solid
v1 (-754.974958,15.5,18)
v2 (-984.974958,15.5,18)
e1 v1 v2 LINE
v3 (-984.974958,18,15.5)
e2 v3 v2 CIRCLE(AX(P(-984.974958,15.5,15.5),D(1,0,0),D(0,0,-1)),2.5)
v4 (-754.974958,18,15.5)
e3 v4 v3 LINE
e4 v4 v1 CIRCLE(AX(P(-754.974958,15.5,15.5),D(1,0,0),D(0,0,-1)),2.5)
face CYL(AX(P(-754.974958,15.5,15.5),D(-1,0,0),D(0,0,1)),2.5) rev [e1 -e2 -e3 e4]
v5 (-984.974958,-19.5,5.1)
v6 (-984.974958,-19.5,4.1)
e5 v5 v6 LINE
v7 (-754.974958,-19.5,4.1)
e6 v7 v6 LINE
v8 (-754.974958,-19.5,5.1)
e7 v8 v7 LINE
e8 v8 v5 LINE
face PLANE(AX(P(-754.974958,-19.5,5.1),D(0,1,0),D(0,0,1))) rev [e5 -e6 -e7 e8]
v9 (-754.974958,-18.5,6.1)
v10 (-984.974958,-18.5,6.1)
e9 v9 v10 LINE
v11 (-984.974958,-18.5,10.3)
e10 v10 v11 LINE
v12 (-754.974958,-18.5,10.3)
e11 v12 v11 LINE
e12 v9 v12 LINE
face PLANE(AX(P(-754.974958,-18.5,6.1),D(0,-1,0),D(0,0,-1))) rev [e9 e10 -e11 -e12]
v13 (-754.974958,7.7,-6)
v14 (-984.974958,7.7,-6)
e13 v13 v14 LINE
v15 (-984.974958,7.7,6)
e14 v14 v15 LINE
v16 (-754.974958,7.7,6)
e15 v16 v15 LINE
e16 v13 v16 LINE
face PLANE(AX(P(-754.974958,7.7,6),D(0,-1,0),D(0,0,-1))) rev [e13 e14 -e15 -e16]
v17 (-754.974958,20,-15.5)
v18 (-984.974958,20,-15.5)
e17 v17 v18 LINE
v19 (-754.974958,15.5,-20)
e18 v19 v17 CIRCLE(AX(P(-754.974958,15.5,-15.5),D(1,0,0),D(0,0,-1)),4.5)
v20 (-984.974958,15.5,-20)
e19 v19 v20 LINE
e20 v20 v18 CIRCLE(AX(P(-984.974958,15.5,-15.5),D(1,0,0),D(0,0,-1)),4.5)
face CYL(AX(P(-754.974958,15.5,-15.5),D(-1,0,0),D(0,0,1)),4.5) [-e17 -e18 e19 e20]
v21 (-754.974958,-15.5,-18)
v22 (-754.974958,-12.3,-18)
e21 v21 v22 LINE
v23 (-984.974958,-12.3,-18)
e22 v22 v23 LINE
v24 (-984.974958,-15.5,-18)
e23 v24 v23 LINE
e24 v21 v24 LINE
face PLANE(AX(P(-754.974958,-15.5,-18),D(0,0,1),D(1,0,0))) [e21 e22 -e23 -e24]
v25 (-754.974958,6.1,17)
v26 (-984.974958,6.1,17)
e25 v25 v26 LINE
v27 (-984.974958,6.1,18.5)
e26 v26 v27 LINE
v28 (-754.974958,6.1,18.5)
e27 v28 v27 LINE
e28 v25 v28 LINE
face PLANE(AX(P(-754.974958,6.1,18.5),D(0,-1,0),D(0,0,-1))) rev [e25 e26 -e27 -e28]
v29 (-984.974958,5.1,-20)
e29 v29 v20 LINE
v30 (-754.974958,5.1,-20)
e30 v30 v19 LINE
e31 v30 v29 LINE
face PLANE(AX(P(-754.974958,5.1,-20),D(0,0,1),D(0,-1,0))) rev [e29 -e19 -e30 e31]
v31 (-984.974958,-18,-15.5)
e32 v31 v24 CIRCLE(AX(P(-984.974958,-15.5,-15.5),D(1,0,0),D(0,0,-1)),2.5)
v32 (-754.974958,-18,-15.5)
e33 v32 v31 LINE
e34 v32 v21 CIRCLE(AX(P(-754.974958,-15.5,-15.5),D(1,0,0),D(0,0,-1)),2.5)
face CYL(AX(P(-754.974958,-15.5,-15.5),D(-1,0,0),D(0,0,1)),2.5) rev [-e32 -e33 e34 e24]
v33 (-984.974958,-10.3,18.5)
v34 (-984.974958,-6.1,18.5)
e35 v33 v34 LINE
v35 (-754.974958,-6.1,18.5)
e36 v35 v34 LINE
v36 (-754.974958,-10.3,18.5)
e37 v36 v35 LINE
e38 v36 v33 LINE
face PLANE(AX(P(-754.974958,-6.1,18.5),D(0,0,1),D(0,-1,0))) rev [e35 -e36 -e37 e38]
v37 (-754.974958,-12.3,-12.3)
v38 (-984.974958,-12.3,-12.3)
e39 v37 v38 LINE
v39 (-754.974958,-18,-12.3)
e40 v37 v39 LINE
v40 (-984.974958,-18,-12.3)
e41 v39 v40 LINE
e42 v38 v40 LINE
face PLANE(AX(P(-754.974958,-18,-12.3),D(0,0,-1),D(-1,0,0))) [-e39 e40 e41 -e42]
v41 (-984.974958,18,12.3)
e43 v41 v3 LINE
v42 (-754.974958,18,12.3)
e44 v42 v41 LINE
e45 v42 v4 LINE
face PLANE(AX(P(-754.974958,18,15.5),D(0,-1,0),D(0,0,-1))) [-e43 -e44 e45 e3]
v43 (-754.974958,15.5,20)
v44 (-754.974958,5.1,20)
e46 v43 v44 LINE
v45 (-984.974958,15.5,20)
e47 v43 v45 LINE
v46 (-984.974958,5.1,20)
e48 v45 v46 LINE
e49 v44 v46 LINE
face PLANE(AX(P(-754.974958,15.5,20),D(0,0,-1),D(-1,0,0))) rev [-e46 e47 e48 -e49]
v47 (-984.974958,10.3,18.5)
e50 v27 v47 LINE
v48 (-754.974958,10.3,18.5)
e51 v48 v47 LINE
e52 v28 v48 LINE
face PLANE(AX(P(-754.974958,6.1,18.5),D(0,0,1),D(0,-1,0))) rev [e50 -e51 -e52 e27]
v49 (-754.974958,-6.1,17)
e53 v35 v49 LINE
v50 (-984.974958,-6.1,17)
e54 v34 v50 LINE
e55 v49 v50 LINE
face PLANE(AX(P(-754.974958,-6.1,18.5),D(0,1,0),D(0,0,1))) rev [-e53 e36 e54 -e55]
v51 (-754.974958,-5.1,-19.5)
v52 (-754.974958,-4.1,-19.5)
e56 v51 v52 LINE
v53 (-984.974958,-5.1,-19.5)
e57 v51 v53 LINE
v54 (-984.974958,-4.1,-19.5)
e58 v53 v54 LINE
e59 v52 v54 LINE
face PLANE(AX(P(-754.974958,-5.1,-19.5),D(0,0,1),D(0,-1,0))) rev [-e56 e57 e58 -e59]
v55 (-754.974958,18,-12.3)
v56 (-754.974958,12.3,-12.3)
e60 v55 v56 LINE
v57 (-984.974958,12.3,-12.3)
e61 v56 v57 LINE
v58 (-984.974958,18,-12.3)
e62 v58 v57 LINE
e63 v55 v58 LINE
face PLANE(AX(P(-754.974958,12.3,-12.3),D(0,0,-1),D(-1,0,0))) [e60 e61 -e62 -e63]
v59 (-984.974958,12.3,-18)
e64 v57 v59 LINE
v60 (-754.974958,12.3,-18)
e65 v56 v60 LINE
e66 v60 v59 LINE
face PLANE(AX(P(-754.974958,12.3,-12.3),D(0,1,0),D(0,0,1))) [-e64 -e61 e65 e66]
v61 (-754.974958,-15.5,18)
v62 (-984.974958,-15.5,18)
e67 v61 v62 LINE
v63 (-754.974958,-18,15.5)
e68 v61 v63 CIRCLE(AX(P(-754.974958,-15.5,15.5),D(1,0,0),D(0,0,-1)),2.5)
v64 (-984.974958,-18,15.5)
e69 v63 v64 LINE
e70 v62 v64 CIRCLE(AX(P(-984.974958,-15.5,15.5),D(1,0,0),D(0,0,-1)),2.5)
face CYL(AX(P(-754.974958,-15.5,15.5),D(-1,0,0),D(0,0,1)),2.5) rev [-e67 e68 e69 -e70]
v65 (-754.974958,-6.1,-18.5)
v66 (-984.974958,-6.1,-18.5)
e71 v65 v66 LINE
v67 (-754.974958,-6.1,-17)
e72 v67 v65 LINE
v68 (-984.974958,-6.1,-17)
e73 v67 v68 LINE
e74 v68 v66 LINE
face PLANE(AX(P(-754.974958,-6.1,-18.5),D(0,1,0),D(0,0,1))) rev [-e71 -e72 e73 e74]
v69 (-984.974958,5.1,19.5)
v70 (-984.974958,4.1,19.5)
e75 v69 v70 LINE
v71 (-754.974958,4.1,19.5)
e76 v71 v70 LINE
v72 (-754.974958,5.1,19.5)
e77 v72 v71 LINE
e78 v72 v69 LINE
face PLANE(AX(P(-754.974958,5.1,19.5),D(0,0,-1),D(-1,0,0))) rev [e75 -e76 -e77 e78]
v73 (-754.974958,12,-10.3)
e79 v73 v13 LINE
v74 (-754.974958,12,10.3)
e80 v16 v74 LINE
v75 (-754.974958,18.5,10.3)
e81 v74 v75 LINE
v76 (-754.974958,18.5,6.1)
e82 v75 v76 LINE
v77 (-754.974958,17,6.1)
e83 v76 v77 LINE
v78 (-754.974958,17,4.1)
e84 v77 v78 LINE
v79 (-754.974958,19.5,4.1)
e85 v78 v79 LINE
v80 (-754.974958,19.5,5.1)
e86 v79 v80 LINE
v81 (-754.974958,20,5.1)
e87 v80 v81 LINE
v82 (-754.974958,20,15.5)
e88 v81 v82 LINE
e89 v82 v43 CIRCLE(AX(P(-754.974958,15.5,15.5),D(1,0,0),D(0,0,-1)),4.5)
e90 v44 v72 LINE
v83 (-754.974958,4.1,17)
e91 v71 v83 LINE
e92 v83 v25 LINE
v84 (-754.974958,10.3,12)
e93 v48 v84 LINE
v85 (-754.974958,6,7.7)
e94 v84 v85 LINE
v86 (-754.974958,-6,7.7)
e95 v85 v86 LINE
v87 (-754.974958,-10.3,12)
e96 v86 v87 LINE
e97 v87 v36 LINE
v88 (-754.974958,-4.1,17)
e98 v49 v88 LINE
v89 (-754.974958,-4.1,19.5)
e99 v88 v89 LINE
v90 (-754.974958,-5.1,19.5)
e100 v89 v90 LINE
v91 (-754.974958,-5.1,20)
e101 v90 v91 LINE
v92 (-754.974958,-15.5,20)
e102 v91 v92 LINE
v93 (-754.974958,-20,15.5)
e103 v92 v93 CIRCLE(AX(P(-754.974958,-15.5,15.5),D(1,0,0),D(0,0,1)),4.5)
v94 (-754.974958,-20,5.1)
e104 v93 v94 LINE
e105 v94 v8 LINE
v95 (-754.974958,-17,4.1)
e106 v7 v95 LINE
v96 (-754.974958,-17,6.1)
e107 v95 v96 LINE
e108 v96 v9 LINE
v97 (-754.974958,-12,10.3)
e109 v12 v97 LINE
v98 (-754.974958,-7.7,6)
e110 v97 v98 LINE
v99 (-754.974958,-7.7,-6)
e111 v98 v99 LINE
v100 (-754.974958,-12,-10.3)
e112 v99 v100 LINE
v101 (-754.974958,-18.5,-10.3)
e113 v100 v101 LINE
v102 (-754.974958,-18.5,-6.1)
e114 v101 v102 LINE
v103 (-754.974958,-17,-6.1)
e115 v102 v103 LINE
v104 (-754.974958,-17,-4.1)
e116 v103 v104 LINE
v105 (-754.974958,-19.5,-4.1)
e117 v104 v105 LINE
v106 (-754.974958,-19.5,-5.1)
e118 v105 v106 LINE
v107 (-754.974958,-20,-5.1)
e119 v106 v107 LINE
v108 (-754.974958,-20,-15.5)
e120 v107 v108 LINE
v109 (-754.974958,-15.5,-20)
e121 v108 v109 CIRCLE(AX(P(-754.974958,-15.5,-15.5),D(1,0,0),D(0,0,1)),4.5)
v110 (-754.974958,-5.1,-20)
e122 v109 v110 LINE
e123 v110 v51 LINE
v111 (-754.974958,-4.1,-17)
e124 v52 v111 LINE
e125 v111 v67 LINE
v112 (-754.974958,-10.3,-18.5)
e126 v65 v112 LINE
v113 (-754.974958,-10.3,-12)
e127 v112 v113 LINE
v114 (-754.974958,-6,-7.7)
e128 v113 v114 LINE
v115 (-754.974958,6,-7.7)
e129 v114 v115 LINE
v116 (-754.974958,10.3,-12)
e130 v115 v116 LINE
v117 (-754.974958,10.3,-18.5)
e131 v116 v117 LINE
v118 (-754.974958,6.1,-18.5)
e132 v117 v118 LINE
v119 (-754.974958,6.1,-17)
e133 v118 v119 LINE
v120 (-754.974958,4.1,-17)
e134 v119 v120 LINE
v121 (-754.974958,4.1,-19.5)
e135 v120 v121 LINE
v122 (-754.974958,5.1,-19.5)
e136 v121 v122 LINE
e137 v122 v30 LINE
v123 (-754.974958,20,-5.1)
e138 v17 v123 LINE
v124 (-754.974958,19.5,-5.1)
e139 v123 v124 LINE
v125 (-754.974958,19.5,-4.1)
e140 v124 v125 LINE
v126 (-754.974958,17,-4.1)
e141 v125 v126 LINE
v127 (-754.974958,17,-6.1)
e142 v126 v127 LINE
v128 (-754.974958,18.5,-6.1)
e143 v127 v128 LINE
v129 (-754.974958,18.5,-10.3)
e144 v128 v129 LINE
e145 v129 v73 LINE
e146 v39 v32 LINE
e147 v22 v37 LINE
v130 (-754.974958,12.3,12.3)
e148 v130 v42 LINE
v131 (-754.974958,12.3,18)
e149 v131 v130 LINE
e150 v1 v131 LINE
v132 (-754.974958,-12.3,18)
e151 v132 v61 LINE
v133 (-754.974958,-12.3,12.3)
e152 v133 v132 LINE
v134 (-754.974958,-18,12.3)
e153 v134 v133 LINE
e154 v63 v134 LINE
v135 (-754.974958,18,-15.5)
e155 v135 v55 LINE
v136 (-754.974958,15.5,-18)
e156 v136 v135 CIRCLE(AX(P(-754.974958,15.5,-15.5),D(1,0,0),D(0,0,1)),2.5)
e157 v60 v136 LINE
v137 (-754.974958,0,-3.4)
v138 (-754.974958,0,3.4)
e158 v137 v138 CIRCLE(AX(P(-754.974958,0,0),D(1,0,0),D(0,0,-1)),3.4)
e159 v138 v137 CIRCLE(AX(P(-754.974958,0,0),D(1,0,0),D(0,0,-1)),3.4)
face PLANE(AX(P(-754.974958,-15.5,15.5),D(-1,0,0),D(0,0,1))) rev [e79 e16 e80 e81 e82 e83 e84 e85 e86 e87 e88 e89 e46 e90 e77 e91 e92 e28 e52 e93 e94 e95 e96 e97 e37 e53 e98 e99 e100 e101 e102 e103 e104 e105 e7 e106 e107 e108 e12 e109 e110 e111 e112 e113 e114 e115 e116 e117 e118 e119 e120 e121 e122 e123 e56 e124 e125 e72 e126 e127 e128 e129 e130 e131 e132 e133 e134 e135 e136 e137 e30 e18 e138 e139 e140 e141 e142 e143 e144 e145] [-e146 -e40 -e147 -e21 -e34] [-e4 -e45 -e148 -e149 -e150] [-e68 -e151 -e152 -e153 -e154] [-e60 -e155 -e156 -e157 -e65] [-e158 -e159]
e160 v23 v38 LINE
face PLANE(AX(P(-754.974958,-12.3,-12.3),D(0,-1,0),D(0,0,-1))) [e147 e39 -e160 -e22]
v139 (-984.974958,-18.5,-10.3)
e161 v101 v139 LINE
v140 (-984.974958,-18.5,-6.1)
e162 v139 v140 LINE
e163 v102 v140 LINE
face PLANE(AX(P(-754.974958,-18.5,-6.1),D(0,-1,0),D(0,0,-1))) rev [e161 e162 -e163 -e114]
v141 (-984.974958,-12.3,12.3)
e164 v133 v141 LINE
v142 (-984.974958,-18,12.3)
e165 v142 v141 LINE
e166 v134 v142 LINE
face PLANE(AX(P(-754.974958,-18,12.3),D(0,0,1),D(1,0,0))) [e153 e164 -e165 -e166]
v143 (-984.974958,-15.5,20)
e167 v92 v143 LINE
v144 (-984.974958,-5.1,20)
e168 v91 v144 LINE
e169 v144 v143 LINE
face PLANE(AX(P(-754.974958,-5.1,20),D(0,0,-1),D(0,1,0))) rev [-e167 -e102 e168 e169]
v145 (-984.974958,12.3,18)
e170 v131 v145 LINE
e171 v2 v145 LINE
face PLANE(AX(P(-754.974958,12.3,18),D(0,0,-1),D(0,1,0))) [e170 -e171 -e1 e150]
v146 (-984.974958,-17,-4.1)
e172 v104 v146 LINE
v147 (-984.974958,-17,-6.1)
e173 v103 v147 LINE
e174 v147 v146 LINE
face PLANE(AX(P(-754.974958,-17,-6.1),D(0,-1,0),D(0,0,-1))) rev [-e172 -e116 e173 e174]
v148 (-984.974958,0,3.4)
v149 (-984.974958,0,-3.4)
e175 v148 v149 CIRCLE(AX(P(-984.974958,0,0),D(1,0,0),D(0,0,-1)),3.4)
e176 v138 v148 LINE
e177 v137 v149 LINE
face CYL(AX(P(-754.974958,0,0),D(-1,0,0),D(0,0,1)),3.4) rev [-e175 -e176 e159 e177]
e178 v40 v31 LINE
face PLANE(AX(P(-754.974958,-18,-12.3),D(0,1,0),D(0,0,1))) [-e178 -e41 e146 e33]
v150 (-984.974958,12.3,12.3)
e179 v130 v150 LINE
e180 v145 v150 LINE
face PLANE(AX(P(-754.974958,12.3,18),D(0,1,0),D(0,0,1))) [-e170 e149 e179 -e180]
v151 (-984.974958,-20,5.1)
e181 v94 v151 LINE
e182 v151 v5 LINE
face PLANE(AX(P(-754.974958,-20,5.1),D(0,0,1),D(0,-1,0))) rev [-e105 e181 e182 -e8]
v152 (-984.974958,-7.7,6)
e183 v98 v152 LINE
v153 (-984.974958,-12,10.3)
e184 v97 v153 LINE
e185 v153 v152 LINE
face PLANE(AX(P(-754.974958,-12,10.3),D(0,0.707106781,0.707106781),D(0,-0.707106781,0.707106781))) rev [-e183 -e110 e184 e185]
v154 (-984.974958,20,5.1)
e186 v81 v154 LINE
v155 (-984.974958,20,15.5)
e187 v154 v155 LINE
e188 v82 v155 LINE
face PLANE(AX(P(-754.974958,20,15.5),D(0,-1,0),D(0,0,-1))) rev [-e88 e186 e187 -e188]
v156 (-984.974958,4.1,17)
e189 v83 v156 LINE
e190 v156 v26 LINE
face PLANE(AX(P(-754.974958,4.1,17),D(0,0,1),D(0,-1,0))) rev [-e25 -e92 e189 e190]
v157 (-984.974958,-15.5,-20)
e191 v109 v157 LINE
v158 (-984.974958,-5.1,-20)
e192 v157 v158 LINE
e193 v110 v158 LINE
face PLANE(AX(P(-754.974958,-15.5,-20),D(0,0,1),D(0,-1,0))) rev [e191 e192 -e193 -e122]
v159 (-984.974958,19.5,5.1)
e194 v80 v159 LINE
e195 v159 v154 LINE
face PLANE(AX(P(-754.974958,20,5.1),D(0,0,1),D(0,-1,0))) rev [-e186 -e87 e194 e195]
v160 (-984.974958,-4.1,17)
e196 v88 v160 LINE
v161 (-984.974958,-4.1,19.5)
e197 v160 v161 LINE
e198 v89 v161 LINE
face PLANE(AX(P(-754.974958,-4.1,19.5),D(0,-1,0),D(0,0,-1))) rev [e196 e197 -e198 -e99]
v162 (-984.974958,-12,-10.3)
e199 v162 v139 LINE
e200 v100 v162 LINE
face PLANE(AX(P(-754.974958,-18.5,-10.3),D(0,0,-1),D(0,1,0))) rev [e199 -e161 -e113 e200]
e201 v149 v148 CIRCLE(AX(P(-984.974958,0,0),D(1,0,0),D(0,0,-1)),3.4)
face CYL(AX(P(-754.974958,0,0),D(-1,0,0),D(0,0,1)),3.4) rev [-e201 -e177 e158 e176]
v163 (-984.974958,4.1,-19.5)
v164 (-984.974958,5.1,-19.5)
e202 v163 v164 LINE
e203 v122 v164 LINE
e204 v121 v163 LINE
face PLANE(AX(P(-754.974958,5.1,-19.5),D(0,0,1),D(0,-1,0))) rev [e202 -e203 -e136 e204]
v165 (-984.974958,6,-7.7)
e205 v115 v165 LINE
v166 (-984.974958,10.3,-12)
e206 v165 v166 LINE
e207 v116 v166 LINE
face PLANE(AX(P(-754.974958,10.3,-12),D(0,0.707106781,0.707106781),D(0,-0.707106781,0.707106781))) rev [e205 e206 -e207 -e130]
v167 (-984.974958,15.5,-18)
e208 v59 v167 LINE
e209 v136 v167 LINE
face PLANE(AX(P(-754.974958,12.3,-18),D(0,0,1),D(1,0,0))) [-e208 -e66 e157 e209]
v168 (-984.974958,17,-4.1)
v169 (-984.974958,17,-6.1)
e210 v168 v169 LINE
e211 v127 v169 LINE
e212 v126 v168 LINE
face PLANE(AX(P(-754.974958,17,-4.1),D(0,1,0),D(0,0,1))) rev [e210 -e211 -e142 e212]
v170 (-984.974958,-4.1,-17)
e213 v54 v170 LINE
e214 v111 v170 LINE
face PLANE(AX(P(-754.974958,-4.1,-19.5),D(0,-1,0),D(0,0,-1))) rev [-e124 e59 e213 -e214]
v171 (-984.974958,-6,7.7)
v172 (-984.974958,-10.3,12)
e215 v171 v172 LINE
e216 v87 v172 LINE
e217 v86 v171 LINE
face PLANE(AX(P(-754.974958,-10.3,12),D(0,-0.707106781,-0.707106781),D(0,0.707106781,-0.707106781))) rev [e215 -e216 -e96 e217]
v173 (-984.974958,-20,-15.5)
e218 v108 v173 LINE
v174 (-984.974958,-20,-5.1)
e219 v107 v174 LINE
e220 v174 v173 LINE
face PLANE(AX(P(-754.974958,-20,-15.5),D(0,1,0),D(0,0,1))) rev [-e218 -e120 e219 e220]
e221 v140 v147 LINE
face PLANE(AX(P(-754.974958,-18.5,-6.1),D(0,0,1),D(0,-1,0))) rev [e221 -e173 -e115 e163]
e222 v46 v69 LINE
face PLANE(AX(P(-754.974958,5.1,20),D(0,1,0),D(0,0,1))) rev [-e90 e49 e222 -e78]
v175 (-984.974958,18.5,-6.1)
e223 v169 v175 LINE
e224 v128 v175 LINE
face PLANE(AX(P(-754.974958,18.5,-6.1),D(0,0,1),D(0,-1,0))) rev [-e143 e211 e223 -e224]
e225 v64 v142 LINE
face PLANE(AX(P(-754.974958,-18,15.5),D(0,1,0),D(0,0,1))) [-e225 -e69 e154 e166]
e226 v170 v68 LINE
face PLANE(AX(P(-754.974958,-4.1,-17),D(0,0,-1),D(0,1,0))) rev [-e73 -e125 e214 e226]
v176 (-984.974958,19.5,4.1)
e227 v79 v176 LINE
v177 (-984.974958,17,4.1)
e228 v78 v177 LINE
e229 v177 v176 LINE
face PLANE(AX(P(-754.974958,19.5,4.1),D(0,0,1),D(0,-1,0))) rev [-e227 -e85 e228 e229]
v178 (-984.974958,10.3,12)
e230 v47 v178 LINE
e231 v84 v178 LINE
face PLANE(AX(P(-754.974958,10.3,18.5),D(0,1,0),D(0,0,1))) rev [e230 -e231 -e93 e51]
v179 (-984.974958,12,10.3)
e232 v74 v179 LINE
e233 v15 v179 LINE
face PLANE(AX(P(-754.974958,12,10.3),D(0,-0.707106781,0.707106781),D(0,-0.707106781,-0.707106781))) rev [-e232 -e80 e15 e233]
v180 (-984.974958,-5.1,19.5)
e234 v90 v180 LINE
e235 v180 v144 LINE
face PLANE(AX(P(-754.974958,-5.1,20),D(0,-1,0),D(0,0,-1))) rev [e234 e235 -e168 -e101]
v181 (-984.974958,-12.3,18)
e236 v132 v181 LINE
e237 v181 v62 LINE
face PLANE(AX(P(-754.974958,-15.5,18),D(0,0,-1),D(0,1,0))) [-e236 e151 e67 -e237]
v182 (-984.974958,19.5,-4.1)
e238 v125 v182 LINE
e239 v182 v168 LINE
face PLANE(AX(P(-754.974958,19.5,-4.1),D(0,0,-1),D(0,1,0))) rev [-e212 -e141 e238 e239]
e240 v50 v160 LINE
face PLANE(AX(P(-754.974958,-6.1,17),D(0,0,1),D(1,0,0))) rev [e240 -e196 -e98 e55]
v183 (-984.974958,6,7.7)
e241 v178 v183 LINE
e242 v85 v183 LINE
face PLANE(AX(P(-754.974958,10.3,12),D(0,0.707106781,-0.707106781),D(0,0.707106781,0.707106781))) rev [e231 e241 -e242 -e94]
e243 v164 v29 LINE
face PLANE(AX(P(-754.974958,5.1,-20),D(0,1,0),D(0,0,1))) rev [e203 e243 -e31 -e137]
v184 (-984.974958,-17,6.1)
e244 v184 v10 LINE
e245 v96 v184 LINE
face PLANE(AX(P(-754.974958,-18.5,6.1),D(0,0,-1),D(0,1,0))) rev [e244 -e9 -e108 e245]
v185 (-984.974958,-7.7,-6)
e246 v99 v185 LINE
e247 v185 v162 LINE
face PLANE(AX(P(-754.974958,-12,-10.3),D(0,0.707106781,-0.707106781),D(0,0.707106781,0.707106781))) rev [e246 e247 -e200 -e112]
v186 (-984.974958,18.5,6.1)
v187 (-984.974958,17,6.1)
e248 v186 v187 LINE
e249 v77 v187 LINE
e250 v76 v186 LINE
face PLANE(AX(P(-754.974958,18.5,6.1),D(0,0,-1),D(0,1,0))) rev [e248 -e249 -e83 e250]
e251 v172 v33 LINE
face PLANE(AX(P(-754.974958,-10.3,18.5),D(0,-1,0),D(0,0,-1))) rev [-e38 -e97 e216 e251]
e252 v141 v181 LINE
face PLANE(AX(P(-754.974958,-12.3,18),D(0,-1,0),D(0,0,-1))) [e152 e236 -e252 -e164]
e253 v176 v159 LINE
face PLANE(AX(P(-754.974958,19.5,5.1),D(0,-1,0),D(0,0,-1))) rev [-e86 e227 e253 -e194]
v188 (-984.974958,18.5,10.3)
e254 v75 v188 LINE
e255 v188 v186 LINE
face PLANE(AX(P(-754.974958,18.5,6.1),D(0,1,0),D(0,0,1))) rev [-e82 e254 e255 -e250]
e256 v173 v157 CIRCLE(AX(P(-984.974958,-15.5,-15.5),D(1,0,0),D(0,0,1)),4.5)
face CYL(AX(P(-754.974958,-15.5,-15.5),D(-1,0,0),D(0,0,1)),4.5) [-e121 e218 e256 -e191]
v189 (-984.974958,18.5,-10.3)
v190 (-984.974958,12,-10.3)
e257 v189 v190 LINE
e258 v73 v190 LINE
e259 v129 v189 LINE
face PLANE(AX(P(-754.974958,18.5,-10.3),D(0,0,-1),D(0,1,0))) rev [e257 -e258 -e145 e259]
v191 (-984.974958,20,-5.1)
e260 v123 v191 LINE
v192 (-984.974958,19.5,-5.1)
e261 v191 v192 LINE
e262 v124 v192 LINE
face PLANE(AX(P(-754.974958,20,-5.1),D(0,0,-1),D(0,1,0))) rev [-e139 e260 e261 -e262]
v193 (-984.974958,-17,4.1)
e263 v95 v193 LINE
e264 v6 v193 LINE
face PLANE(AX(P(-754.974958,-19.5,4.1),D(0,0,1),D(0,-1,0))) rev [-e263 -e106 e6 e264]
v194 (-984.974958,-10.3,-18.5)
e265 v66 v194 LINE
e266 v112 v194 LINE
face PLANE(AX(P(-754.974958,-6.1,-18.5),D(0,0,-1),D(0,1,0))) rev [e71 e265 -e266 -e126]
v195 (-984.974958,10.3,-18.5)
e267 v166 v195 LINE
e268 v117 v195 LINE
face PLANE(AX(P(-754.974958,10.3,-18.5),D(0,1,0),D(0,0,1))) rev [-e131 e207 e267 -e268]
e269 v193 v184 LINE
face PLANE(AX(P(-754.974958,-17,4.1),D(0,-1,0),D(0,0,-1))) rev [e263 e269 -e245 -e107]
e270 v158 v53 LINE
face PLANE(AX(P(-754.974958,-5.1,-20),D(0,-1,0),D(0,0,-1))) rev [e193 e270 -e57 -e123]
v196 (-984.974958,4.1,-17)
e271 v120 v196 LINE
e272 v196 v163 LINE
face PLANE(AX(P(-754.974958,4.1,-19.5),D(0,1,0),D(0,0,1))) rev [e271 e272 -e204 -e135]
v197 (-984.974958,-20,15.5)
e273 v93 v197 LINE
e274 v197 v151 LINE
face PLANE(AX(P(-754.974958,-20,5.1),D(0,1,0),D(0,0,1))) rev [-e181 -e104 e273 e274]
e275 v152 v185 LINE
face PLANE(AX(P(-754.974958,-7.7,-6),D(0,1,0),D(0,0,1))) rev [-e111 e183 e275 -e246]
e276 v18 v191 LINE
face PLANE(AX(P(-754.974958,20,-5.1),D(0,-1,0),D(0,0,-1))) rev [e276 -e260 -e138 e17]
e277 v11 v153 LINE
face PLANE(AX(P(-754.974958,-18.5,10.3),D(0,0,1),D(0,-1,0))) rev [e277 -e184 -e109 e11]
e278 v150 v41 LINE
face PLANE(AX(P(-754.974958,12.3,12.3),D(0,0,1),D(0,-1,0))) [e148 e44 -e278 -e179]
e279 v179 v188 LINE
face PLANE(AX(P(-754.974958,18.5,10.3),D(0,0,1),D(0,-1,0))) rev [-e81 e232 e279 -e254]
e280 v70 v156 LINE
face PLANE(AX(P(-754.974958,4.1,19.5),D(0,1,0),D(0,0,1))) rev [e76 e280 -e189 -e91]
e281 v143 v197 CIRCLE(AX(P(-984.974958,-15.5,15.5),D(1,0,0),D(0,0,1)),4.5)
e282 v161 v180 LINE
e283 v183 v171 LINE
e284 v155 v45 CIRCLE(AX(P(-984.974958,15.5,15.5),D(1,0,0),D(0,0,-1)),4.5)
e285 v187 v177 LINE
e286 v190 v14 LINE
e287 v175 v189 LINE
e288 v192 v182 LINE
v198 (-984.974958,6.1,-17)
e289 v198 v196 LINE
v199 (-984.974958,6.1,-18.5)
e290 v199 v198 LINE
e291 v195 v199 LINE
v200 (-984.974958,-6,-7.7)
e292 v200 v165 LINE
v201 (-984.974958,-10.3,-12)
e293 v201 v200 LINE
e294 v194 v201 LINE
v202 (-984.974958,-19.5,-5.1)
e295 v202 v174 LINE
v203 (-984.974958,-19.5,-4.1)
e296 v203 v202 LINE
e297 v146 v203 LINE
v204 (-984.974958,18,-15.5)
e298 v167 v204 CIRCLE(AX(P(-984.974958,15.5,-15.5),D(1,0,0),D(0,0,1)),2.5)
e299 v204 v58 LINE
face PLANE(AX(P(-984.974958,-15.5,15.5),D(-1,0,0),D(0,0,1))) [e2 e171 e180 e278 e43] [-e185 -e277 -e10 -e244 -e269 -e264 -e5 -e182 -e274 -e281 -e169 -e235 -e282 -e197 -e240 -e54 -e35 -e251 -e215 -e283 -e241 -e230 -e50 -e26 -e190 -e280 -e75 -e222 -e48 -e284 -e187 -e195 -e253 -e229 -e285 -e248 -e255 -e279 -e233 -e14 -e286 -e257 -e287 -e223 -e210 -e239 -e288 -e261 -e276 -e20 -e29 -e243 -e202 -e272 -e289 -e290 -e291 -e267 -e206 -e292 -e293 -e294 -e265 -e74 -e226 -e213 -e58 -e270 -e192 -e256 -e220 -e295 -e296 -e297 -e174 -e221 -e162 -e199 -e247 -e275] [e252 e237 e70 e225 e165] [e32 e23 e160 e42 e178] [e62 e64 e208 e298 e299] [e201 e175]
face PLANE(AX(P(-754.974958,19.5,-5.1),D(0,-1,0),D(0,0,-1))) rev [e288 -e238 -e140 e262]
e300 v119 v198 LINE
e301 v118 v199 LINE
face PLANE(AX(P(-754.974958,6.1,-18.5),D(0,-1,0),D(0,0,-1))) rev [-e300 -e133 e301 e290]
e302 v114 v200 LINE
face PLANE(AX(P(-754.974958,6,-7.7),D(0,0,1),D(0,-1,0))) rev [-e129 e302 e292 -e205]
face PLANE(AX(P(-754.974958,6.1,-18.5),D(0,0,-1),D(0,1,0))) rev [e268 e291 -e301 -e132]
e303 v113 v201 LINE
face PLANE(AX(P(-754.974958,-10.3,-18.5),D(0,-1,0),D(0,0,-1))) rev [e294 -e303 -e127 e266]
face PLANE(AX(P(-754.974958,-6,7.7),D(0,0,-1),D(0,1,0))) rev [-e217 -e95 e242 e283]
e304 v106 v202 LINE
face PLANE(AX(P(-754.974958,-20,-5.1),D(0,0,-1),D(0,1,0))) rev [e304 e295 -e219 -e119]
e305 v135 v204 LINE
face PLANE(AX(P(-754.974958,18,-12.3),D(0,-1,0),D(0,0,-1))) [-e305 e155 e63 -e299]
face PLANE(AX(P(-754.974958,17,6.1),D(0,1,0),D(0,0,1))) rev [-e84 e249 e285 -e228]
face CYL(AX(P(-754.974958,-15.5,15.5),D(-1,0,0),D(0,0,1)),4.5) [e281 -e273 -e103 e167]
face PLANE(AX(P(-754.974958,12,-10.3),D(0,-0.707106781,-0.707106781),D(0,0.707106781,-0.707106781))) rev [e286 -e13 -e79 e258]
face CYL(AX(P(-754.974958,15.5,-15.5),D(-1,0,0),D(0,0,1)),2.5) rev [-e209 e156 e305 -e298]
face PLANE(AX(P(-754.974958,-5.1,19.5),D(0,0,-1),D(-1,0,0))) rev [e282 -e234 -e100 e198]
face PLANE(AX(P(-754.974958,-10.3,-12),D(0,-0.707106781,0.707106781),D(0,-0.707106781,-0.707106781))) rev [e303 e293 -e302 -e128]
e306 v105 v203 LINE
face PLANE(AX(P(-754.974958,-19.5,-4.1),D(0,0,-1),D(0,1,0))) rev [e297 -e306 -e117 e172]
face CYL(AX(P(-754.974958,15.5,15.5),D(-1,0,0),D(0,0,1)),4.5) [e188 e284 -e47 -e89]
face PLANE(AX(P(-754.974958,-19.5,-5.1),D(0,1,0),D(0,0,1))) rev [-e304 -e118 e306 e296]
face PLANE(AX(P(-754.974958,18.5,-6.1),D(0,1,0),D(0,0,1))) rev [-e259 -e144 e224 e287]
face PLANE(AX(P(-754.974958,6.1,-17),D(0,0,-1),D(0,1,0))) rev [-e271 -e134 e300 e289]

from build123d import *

# Parameters (mm, degrees)
SKETCH1_R                                 = 3.4
ALUMINIUM_PROFILE_40_X_40B_X_R4_5_1_DEPTH = 230


with BuildPart() as part:
    # Sketch1 → Aluminium profile 40 X 40B X R4.5(1) (new body)
    with BuildSketch(Plane.YZ.offset(-984.974958264)):
        with BuildLine():
            Line((-5.1, 20), (-5.1, 19.5))
            Line((-5.1, 19.5), (-4.1, 19.5))
            Line((-4.1, 19.5), (-4.1, 17))
            Line((-4.1, 17), (-6.1, 17))
            Line((-6.1, 17), (-6.1, 18.5))
            Line((-6.1, 18.5), (-10.3, 18.5))
            Line((-10.3, 18.5), (-10.3, 12))
            Line((-10.3, 12), (-6, 7.7))
            Line((-6, 7.7), (6, 7.7))
            Line((6, 7.7), (10.3, 12))
            Line((10.3, 12), (10.3, 18.5))
            Line((10.3, 18.5), (6.1, 18.5))
            Line((6.1, 18.5), (6.1, 17))
            Line((6.1, 17), (4.1, 17))
            Line((4.1, 17), (4.1, 19.5))
            Line((4.1, 19.5), (5.1, 19.5))
            Line((5.1, 19.5), (5.1, 20))
            Line((5.1, 20), (15.5, 20))
            ThreePointArc((15.5, 20), (18.681980515, 18.681980515), (20, 15.5))
            Line((20, 15.5), (20, 5.1))
            Line((20, 5.1), (19.5, 5.1))
            Line((19.5, 5.1), (19.5, 4.1))
            Line((19.5, 4.1), (17, 4.1))
            Line((17, 4.1), (17, 6.1))
            Line((17, 6.1), (18.5, 6.1))
            Line((18.5, 6.1), (18.5, 10.3))
            Line((18.5, 10.3), (12, 10.3))
            Line((12, 10.3), (7.7, 6))
            Line((7.7, 6), (7.7, -6))
            Line((7.7, -6), (12, -10.3))
            Line((12, -10.3), (18.5, -10.3))
            Line((18.5, -10.3), (18.5, -6.1))
            Line((18.5, -6.1), (17, -6.1))
            Line((17, -6.1), (17, -4.1))
            Line((17, -4.1), (19.5, -4.1))
            Line((19.5, -4.1), (19.5, -5.1))
            Line((19.5, -5.1), (20, -5.1))
            Line((20, -5.1), (20, -15.5))
            ThreePointArc((20, -15.5), (18.681980515, -18.681980515), (15.5, -20))
            Line((15.5, -20), (5.1, -20))
            Line((5.1, -20), (5.1, -19.5))
            Line((5.1, -19.5), (4.1, -19.5))
            Line((4.1, -19.5), (4.1, -17))
            Line((4.1, -17), (6.1, -17))
            Line((6.1, -17), (6.1, -18.5))
            Line((6.1, -18.5), (10.3, -18.5))
            Line((10.3, -18.5), (10.3, -12))
            Line((10.3, -12), (6, -7.7))
            Line((6, -7.7), (-6, -7.7))
            Line((-6, -7.7), (-10.3, -12))
            Line((-10.3, -12), (-10.3, -18.5))
            Line((-10.3, -18.5), (-6.1, -18.5))
            Line((-6.1, -18.5), (-6.1, -17))
            Line((-6.1, -17), (-4.1, -17))
            Line((-4.1, -17), (-4.1, -19.5))
            Line((-4.1, -19.5), (-5.1, -19.5))
            Line((-5.1, -19.5), (-5.1, -20))
            Line((-5.1, -20), (-15.5, -20))
            ThreePointArc((-15.5, -20), (-18.681980515, -18.681980515), (-20, -15.5))
            Line((-20, -15.5), (-20, -5.1))
            Line((-20, -5.1), (-19.5, -5.1))
            Line((-19.5, -5.1), (-19.5, -4.1))
            Line((-19.5, -4.1), (-17, -4.1))
            Line((-17, -4.1), (-17, -6.1))
            Line((-17, -6.1), (-18.5, -6.1))
            Line((-18.5, -6.1), (-18.5, -10.3))
            Line((-18.5, -10.3), (-12, -10.3))
            Line((-12, -10.3), (-7.7, -6))
            Line((-7.7, -6), (-7.7, 6))
            Line((-7.7, 6), (-12, 10.3))
            Line((-12, 10.3), (-18.5, 10.3))
            Line((-18.5, 10.3), (-18.5, 6.1))
            Line((-18.5, 6.1), (-17, 6.1))
            Line((-17, 6.1), (-17, 4.1))
            Line((-17, 4.1), (-19.5, 4.1))
            Line((-19.5, 4.1), (-19.5, 5.1))
            Line((-19.5, 5.1), (-20, 5.1))
            Line((-20, 5.1), (-20, 15.5))
            ThreePointArc((-20, 15.5), (-18.681980515, 18.681980515), (-15.5, 20))
            Line((-15.5, 20), (-5.1, 20))
        make_face()
        Circle(SKETCH1_R, mode=Mode.SUBTRACT)
        with BuildLine():
            Line((12.3, 18), (15.5, 18))
            ThreePointArc((15.5, 18), (17.267766953, 17.267766953), (18, 15.5))
            Line((18, 15.5), (18, 12.3))
            Line((18, 12.3), (12.3, 12.3))
            Line((12.3, 12.3), (12.3, 18))
        make_face(mode=Mode.SUBTRACT)
        with BuildLine():
            Line((-15.5, 18), (-12.3, 18))
            Line((-12.3, 18), (-12.3, 12.3))
            Line((-12.3, 12.3), (-18, 12.3))
            Line((-18, 12.3), (-18, 15.5))
            ThreePointArc((-18, 15.5), (-17.267766953, 17.267766953), (-15.5, 18))
        make_face(mode=Mode.SUBTRACT)
        with BuildLine():
            Line((-18, -12.3), (-12.3, -12.3))
            Line((-12.3, -12.3), (-12.3, -18))
            Line((-12.3, -18), (-15.5, -18))
            ThreePointArc((-15.5, -18), (-17.267766953, -17.267766953), (-18, -15.5))
            Line((-18, -15.5), (-18, -12.3))
        make_face(mode=Mode.SUBTRACT)
        with BuildLine():
            Line((12.3, -12.3), (18, -12.3))
            Line((18, -12.3), (18, -15.5))
            ThreePointArc((18, -15.5), (17.267766953, -17.267766953), (15.5, -18))
            Line((15.5, -18), (12.3, -18))
            Line((12.3, -18), (12.3, -12.3))
        make_face(mode=Mode.SUBTRACT)
    extrude(amount=ALUMINIUM_PROFILE_40_X_40B_X_R4_5_1_DEPTH)


solid = part.part
